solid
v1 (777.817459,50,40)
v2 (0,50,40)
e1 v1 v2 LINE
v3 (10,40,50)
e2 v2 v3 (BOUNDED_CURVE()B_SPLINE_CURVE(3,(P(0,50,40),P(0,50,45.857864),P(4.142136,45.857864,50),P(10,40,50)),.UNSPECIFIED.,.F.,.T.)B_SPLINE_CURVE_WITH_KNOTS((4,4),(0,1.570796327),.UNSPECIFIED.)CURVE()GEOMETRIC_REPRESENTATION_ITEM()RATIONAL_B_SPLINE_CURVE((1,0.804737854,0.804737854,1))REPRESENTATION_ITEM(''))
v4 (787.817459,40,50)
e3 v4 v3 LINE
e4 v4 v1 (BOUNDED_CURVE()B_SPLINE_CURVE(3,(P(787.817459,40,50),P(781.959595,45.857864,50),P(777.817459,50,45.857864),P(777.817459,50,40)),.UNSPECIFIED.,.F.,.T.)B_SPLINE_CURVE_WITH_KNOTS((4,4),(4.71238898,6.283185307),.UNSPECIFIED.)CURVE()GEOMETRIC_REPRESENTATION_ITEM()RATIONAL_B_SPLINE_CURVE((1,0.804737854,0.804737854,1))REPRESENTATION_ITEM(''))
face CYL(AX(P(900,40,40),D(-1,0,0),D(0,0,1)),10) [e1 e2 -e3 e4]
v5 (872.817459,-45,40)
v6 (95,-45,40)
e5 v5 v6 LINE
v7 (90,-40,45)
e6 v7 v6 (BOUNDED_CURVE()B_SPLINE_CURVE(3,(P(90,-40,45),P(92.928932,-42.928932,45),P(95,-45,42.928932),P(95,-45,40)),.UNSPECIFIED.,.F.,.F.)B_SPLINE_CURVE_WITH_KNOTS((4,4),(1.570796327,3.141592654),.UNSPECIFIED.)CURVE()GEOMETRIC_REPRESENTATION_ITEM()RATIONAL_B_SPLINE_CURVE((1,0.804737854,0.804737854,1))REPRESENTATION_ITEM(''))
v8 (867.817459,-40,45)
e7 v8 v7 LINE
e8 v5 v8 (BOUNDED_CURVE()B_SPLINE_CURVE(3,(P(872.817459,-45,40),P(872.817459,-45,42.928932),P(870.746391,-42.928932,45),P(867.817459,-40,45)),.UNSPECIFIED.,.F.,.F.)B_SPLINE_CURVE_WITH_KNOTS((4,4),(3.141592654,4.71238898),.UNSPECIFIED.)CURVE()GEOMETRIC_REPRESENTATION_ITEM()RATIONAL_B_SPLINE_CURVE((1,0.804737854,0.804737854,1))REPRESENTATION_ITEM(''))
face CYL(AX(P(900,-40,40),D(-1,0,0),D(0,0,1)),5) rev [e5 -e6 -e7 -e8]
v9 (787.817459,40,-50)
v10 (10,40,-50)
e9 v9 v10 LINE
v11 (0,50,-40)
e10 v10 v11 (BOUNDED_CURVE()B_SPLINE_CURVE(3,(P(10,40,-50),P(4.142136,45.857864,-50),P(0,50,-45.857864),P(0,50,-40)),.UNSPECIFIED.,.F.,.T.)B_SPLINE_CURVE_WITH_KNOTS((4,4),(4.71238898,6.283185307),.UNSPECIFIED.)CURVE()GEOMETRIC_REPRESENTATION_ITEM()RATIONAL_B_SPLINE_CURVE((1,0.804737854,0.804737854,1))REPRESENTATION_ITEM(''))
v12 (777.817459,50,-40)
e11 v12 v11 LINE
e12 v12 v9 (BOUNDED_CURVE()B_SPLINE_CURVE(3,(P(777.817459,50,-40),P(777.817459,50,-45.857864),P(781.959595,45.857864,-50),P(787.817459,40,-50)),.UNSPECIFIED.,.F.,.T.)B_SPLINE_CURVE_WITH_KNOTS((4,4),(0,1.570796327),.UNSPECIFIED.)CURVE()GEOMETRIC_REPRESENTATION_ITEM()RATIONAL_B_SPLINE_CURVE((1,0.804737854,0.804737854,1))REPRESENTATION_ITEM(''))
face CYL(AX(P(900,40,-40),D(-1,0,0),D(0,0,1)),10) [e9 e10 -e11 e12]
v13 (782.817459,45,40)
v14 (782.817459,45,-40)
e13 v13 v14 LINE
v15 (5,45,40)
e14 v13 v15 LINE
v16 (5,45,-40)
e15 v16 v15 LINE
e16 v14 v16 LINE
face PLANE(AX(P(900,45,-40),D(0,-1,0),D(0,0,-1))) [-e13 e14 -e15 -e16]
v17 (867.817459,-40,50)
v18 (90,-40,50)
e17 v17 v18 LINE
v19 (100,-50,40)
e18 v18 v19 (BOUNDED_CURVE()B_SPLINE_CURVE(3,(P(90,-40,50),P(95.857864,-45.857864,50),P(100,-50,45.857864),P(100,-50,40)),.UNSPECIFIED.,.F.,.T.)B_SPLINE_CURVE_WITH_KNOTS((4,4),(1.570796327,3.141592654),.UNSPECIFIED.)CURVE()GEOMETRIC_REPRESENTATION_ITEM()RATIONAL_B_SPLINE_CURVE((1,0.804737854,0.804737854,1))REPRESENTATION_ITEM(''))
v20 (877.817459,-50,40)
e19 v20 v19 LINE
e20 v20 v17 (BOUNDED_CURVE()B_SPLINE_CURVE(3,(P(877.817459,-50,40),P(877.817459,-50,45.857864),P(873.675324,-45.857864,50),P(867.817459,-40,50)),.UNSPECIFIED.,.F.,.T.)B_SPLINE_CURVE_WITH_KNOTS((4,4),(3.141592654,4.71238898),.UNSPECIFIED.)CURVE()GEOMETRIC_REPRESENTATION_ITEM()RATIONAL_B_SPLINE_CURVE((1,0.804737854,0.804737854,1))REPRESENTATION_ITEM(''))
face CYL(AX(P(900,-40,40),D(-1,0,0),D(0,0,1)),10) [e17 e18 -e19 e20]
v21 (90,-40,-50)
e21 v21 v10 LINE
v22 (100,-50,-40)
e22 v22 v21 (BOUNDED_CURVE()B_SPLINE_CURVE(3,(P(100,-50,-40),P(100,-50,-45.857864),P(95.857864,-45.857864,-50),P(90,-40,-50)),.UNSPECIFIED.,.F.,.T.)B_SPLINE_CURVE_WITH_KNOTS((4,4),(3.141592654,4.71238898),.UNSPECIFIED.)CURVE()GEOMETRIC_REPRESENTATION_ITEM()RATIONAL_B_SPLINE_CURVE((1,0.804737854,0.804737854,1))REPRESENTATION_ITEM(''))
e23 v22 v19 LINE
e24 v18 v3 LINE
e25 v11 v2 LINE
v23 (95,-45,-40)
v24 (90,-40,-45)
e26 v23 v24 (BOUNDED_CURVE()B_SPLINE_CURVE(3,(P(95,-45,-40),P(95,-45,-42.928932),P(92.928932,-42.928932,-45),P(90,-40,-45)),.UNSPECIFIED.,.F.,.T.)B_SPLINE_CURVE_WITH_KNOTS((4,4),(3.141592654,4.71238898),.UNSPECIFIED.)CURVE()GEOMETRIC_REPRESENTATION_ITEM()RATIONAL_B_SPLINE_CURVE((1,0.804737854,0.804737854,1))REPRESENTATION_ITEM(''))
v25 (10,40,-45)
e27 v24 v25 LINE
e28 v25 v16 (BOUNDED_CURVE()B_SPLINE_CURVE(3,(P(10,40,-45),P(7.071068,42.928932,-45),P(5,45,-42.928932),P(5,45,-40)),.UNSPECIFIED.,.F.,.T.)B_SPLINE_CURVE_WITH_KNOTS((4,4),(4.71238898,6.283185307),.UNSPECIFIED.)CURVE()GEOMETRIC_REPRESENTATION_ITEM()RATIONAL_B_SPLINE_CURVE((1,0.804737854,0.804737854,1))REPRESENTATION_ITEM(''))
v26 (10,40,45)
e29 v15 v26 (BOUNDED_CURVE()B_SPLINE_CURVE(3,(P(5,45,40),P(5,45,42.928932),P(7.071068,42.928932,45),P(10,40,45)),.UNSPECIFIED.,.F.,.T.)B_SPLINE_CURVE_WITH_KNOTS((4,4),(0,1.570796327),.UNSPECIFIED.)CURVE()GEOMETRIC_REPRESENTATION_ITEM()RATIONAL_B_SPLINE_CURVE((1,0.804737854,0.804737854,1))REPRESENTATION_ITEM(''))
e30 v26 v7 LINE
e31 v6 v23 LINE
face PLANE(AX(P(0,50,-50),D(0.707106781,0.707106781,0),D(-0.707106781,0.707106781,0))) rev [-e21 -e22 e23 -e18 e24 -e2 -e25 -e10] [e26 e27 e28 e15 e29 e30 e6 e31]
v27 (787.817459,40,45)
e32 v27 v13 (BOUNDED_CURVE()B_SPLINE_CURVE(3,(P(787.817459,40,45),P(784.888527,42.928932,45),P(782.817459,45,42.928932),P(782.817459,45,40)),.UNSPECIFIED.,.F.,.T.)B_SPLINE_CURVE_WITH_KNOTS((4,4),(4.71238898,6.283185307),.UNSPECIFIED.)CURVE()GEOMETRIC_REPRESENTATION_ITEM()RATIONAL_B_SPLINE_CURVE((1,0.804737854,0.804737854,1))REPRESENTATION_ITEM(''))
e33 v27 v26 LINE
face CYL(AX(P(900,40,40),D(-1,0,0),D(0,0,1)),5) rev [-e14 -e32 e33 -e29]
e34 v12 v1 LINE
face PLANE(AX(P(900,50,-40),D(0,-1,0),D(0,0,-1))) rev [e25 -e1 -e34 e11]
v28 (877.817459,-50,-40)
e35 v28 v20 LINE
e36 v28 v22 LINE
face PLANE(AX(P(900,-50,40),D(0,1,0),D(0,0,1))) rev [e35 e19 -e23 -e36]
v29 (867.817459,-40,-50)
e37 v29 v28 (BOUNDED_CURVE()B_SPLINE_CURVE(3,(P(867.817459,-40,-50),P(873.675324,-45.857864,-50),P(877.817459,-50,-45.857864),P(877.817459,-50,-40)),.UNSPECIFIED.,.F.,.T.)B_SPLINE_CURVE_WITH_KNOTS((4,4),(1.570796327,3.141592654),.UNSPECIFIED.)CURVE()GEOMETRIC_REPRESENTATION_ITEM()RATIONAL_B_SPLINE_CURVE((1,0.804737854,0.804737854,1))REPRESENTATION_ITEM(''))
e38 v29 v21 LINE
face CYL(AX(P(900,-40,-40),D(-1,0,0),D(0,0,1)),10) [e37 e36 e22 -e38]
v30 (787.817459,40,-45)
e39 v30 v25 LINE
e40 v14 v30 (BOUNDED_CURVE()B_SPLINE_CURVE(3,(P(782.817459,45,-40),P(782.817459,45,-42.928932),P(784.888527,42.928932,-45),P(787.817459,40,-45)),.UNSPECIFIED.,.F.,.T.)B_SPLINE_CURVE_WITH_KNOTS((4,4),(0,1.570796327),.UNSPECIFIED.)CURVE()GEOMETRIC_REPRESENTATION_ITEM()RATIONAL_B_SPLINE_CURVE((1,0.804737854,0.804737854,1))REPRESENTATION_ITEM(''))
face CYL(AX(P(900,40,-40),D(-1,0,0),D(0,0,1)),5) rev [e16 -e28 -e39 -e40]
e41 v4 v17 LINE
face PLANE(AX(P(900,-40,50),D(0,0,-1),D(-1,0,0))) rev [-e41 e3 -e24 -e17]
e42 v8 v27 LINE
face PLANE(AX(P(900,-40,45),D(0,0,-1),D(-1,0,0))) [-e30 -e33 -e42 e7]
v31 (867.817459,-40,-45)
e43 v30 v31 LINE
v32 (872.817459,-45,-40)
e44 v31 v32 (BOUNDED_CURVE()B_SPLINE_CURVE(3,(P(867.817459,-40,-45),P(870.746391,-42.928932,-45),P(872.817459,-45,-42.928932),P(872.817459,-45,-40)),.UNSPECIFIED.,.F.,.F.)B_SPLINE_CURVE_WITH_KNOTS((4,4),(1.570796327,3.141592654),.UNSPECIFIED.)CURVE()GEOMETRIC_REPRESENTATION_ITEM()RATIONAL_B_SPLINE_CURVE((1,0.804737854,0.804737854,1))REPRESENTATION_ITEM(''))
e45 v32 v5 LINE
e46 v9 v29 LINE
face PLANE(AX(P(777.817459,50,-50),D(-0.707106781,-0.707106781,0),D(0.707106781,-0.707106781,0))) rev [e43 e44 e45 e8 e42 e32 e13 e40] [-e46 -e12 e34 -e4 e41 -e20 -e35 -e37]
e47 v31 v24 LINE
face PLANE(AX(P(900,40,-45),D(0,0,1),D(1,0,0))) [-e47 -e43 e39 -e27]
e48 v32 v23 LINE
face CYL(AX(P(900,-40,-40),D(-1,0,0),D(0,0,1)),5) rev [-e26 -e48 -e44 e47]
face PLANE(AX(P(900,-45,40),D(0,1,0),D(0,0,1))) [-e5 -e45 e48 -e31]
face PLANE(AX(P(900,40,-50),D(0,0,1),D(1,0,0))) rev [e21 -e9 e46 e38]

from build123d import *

# Parameters (mm, degrees)
F_100_X_100_X_5_1_DEPTH = 900
CUT_EXTRUDE_1_DEPTH     = 100


with BuildPart() as part:
    # Sketch1 → 方形管 100 X 100 X 5(1) (new body)
    with BuildSketch(Plane(origin=(0, 0, 0), x_dir=(0, 0, -1), z_dir=(1, 0, 0))):
        with BuildLine():
            Line((-40, -50), (40, -50))
            ThreePointArc((40, -50), (47.071067812, -47.071067812), (50, -40))
            Line((50, -40), (50, 40))
            ThreePointArc((50, 40), (47.071067812, 47.071067812), (40, 50))
            Line((40, 50), (-40, 50))
            ThreePointArc((-40, 50), (-47.071067812, 47.071067812), (-50, 40))
            Line((-50, 40), (-50, -40))
            ThreePointArc((-50, -40), (-47.071067812, -47.071067812), (-40, -50))
        make_face()
        with BuildLine():
            Line((-40, -45), (40, -45))
            ThreePointArc((40, -45), (43.535533906, -43.535533906), (45, -40))
            Line((45, -40), (45, 40))
            ThreePointArc((45, 40), (43.535533906, 43.535533906), (40, 45))
            Line((40, 45), (-40, 45))
            ThreePointArc((-40, 45), (-43.535533906, 43.535533906), (-45, 40))
            Line((-45, 40), (-45, -40))
            ThreePointArc((-45, -40), (-43.535533906, -43.535533906), (-40, -45))
        make_face(mode=Mode.SUBTRACT)
    extrude(amount=F_100_X_100_X_5_1_DEPTH)

    # 草图2 → 切除-拉伸1 (cut)
    with BuildSketch(Plane.XY.offset(50)):
        Polygon((0, 50), (100, -50), (0, -50), align=None)
        Polygon((913.789188304, -85.971728999), (913.789188304, 50), (777.817459305, 50), align=None)
    extrude(amount=-CUT_EXTRUDE_1_DEPTH, mode=Mode.SUBTRACT)


solid = part.part
